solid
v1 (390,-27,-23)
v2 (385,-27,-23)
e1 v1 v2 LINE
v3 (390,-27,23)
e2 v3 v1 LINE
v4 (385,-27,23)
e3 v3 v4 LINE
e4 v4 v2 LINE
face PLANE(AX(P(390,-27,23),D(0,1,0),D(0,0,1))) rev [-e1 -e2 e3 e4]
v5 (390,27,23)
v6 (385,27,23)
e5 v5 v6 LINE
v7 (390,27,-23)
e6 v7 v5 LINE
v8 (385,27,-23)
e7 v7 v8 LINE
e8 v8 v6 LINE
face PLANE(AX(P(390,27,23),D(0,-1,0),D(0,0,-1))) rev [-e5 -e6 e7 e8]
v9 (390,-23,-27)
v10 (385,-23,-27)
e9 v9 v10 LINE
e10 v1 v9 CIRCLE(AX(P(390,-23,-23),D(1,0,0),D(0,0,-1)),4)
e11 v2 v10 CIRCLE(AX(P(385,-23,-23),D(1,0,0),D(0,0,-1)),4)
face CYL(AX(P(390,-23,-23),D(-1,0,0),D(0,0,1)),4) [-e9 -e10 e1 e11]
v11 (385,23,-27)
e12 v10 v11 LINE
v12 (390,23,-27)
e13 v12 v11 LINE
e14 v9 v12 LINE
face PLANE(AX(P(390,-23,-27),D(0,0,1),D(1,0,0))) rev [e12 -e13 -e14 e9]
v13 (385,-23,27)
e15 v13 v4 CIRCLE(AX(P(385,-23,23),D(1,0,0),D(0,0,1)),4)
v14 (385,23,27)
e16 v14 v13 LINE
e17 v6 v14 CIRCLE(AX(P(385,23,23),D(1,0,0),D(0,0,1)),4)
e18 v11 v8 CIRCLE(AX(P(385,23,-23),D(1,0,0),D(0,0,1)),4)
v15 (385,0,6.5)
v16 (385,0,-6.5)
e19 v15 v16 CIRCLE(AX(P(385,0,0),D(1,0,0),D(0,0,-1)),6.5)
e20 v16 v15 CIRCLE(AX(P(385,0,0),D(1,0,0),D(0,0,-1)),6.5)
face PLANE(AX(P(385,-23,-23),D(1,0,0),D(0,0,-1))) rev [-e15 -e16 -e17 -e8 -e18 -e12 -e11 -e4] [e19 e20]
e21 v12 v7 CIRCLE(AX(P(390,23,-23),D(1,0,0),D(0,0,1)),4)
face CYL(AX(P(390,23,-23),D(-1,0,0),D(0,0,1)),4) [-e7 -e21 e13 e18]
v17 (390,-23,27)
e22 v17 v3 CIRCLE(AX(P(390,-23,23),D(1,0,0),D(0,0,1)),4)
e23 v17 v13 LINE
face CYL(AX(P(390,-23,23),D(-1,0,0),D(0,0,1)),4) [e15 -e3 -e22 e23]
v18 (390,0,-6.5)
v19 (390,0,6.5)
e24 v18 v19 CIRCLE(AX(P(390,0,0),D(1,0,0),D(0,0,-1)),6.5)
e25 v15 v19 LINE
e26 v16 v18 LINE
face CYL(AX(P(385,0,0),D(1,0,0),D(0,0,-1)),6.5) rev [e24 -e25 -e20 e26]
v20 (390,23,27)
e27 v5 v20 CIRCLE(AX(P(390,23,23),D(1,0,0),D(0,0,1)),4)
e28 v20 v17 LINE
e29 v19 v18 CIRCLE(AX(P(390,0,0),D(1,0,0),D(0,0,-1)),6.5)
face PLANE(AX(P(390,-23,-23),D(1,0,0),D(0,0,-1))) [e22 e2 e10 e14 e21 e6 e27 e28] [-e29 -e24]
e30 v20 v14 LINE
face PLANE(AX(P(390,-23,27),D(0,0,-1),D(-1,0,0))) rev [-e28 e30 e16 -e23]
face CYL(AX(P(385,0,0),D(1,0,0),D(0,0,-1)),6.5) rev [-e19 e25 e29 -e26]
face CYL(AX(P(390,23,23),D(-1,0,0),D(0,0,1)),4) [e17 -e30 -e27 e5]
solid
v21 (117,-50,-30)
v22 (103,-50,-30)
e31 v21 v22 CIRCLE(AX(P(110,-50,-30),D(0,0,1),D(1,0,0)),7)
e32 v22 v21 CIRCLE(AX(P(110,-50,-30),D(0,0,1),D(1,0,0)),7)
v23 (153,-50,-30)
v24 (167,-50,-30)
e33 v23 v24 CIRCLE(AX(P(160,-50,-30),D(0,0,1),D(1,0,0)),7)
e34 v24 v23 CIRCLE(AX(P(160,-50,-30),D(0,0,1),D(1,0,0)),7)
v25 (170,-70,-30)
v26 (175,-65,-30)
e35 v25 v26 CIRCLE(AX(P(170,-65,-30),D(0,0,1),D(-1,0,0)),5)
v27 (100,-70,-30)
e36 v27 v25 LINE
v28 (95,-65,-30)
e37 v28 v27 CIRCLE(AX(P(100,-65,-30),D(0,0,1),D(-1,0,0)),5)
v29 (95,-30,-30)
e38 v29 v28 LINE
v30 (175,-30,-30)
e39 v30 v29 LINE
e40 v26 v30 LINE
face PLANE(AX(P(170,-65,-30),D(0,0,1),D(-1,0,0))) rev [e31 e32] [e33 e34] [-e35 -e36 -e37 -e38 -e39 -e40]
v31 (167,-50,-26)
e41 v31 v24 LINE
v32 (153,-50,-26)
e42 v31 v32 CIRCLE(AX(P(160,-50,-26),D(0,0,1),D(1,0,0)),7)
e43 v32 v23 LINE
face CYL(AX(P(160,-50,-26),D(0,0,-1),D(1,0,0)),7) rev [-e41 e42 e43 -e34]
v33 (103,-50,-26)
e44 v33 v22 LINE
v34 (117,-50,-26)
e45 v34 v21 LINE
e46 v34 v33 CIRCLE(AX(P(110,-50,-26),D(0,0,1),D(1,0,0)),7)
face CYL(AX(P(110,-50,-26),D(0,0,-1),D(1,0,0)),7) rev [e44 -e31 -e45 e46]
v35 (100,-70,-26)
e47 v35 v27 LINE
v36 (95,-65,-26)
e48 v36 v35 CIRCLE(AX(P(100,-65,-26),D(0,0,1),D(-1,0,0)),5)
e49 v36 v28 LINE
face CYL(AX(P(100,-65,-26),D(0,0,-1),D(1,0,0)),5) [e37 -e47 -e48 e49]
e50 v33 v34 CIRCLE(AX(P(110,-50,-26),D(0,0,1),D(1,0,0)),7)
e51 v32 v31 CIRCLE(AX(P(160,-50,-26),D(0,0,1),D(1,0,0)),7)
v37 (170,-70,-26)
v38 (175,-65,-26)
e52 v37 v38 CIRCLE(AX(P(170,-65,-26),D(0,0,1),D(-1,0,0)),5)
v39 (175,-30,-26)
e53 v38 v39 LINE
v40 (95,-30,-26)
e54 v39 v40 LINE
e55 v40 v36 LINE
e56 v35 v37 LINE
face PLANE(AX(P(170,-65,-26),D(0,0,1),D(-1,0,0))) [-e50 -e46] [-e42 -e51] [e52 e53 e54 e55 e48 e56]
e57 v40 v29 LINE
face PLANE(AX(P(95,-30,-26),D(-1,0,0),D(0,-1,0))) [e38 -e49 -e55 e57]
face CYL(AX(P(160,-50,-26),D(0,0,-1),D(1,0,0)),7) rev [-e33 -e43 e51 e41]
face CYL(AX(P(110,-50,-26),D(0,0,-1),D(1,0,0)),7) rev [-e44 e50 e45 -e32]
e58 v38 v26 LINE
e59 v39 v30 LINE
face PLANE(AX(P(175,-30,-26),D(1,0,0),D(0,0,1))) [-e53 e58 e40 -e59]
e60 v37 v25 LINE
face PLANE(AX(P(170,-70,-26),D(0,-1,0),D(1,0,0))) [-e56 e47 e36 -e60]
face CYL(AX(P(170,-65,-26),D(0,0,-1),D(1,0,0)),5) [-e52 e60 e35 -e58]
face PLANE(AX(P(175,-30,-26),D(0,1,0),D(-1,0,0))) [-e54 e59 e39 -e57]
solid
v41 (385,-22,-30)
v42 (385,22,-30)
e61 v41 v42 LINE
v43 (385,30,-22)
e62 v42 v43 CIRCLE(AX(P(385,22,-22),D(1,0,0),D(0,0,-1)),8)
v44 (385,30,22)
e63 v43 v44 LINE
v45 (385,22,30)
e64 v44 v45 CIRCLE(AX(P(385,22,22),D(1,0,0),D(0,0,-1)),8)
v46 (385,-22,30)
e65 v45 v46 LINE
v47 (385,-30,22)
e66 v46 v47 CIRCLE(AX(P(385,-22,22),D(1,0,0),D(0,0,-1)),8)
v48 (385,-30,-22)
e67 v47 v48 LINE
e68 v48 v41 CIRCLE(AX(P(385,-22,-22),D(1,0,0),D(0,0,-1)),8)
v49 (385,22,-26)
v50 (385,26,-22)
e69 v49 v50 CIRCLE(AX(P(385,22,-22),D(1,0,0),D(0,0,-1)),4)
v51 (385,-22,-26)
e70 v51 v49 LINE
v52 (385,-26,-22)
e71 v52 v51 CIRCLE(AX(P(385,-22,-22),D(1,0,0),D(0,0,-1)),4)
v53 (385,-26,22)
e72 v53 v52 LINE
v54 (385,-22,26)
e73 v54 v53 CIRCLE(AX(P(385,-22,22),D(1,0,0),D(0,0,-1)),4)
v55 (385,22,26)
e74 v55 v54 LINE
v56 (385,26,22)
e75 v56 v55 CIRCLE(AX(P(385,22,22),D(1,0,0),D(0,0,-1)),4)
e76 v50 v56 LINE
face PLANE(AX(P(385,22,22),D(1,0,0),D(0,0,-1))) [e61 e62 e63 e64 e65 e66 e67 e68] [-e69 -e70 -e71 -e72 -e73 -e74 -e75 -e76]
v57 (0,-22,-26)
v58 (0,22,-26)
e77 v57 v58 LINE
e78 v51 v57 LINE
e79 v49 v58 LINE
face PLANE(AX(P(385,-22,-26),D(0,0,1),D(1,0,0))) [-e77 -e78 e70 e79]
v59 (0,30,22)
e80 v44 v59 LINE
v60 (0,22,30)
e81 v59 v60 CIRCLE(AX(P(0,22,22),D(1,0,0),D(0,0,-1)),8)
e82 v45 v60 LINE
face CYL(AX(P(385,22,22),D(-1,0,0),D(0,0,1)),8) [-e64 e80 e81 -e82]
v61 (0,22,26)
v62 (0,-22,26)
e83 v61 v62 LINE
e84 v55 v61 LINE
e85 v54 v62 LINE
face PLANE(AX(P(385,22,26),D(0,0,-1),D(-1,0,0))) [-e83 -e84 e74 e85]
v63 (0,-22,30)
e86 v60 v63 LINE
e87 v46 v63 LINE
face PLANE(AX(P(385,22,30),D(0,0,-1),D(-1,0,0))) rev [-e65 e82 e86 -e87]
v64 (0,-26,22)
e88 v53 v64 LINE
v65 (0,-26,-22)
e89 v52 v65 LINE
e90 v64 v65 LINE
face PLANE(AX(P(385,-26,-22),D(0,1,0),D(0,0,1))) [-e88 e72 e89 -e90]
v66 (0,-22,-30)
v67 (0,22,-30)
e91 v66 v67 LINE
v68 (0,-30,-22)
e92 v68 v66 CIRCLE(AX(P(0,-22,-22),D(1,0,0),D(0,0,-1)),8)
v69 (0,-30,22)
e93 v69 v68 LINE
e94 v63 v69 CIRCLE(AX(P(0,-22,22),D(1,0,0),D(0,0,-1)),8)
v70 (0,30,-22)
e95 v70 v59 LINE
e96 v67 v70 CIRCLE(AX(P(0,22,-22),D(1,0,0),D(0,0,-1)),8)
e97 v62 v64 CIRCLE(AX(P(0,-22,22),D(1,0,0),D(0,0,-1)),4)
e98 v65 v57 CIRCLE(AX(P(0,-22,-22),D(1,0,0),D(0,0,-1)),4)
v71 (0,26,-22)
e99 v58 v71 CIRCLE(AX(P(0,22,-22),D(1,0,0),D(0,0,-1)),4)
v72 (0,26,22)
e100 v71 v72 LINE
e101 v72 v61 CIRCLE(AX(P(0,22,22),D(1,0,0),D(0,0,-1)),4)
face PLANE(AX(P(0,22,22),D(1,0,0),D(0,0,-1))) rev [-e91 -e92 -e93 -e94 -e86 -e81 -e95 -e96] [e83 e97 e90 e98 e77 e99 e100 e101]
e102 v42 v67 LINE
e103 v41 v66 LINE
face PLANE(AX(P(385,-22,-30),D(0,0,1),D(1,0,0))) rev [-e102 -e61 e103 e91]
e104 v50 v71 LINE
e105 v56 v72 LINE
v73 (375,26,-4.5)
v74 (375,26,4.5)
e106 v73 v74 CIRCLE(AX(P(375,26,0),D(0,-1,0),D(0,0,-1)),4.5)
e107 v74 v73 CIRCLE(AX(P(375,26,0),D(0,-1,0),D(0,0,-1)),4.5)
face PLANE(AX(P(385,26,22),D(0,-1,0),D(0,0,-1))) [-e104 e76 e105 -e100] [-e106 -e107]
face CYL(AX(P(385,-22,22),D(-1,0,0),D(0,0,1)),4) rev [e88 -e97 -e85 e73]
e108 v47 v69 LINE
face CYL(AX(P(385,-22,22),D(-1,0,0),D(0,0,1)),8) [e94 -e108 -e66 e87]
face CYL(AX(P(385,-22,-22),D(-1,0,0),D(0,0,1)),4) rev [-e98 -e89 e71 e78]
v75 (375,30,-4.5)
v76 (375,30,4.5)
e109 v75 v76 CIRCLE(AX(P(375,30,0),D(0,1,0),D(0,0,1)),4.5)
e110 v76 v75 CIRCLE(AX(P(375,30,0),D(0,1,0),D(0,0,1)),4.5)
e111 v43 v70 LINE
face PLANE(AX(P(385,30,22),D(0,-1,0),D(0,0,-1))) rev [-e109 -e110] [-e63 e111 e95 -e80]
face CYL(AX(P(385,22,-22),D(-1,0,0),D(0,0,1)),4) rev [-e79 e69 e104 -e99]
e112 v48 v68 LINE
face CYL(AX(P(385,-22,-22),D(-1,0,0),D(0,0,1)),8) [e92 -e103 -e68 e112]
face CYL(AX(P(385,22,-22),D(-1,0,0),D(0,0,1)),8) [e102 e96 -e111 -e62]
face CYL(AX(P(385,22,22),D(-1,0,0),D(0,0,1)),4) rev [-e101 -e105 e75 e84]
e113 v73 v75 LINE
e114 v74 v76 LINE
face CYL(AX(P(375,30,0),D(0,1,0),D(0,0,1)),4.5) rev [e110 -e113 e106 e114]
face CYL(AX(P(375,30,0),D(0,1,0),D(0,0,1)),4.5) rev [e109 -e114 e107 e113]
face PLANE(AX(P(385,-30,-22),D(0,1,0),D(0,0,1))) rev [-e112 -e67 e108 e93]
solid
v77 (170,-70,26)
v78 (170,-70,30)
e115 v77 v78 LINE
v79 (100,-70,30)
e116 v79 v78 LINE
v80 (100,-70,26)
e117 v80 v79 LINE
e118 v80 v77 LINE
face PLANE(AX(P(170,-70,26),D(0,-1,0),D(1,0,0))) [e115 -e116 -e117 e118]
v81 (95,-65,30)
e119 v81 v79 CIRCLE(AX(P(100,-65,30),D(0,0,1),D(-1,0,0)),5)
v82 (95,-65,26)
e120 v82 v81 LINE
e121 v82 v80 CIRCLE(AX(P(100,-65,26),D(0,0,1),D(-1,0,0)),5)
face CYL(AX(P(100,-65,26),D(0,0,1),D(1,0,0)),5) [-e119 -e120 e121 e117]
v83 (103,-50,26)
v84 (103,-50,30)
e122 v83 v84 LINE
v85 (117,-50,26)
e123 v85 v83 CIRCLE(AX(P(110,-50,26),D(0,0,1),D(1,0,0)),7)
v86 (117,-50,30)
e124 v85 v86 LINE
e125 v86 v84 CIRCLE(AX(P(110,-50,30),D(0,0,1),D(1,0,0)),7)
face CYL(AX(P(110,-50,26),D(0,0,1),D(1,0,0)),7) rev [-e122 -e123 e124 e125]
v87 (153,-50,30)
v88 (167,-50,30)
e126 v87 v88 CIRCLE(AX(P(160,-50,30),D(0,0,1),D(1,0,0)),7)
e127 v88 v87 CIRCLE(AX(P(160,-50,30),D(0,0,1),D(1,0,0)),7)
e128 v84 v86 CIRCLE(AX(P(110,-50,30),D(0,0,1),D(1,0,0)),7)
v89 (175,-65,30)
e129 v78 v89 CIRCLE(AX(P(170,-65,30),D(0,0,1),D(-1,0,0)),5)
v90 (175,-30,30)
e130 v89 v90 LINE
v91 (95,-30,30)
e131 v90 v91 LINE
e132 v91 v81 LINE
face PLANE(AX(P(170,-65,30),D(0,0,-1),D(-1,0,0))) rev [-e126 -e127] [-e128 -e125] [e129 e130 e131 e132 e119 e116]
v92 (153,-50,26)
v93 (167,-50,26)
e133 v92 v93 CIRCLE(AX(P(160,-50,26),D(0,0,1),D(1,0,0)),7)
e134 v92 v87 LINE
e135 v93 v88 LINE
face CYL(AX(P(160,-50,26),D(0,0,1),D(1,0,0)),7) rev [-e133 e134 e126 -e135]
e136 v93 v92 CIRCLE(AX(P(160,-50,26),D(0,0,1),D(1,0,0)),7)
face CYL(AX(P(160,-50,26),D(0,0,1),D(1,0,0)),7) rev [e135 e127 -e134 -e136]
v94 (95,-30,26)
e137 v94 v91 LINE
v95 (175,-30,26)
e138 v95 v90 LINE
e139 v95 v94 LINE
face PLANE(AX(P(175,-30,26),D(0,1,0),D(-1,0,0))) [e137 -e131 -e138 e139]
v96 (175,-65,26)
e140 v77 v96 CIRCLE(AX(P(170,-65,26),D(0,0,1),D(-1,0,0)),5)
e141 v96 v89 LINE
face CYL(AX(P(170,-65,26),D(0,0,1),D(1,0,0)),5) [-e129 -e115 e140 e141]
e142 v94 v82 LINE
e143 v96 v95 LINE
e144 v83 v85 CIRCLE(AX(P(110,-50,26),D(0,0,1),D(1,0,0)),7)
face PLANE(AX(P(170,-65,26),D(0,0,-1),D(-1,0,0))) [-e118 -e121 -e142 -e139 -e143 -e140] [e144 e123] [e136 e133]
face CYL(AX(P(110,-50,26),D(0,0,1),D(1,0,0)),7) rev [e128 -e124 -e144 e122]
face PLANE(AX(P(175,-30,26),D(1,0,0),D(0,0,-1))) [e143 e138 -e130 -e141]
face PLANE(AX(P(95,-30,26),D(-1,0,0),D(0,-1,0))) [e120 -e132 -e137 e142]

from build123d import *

# Parameters (mm, degrees)
GB_T6728_2002_60_X_60_X_4_1_DEPTH = 385
EXTRUDE_1_DEPTH                   = 5
SKETCH_4_R                        = 7
EXTRUDE_2_DEPTH                   = 4
SKETCH_5_R                        = 6.5
CUT_EXTRUDE_1_DEPTH               = 5


with BuildPart() as part:
    # Sketch1 → 冷弯空心方管gb∕t6728-2002 60 X 60 X 4(1) (new body)
    with BuildSketch(Plane.YZ):
        with BuildLine():
            Line((-22, -30), (22, -30))
            ThreePointArc((22, -30), (27.656854249, -27.656854249), (30, -22))
            Line((30, -22), (30, 22))
            ThreePointArc((30, 22), (27.656854249, 27.656854249), (22, 30))
            Line((22, 30), (-22, 30))
            ThreePointArc((-22, 30), (-27.656854249, 27.656854249), (-30, 22))
            Line((-30, 22), (-30, -22))
            ThreePointArc((-30, -22), (-27.656854249, -27.656854249), (-22, -30))
        make_face()
        with BuildLine():
            Line((-22, -26), (22, -26))
            ThreePointArc((22, -26), (24.828427125, -24.828427125), (26, -22))
            Line((26, -22), (26, 22))
            ThreePointArc((26, 22), (24.828427125, 24.828427125), (22, 26))
            Line((22, 26), (-22, 26))
            ThreePointArc((-22, 26), (-24.828427125, 24.828427125), (-26, 22))
            Line((-26, 22), (-26, -22))
            ThreePointArc((-26, -22), (-24.828427125, -24.828427125), (-22, -26))
        make_face(mode=Mode.SUBTRACT)
    extrude(amount=GB_T6728_2002_60_X_60_X_4_1_DEPTH)

    # 草图8 → M10x1.0 螺纹孔1 (revolve, cut)
    with BuildSketch(Plane(origin=(375, 30, 0), x_dir=(0, 0, 1), z_dir=(1, 0, 0))):
        Polygon((0, 0), (0, 10.703872786), (4.5, 8), (4.5, 0), align=None)
    revolve(axis=Axis((375, 36.35, 0), (0, -1, 0)), mode=Mode.SUBTRACT)


with BuildPart() as body_2:
    # 草图3 → 凸台-拉伸1 (new body)
    with BuildSketch(Plane(origin=(385, 0, 0), x_dir=(0, 0, -1), z_dir=(1, 0, 0))):
        with BuildLine():
            Line((-23, -27), (23, -27))
            ThreePointArc((23, -27), (25.828427125, -25.828427125), (27, -23))
            Line((27, -23), (27, 23))
            ThreePointArc((27, 23), (25.828427125, 25.828427125), (23, 27))
            Line((23, 27), (-23, 27))
            ThreePointArc((-23, 27), (-25.828427125, 25.828427125), (-27, 23))
            Line((-27, 23), (-27, -23))
            ThreePointArc((-27, -23), (-25.828427125, -25.828427125), (-23, -27))
        make_face()
    extrude(amount=EXTRUDE_1_DEPTH)

    # 草图5 → 切除-拉伸1 (cut)
    with BuildSketch(Plane(origin=(390, 0, 0), x_dir=(0, 0, -1), z_dir=(1, 0, 0))):
        Circle(SKETCH_5_R)
    extrude(amount=-CUT_EXTRUDE_1_DEPTH, mode=Mode.SUBTRACT)


with BuildPart() as body_3:
    # 草图4 → 凸台-拉伸2 (new body)
    with BuildSketch(Plane.XY.offset(30)):
        with BuildLine():
            Line((175, -30), (95, -30))
            Line((95, -30), (95, -65))
            ThreePointArc((95, -65), (96.464466094, -68.535533906), (100, -70))
            Line((100, -70), (170, -70))
            ThreePointArc((170, -70), (173.535533906, -68.535533906), (175, -65))
            Line((175, -65), (175, -30))
        make_face()
        with Locations((110, -50)):
            Circle(SKETCH_4_R, mode=Mode.SUBTRACT)
        with Locations((160, -50)):
            Circle(SKETCH_4_R, mode=Mode.SUBTRACT)
    extrude(amount=-EXTRUDE_2_DEPTH)


with BuildPart() as body_4:
    # 镜向2: mirrored copy
    add(body_3.part.mirror(Plane.XY))


solid = Compound([part.part, body_2.part, body_3.part, body_4.part])
